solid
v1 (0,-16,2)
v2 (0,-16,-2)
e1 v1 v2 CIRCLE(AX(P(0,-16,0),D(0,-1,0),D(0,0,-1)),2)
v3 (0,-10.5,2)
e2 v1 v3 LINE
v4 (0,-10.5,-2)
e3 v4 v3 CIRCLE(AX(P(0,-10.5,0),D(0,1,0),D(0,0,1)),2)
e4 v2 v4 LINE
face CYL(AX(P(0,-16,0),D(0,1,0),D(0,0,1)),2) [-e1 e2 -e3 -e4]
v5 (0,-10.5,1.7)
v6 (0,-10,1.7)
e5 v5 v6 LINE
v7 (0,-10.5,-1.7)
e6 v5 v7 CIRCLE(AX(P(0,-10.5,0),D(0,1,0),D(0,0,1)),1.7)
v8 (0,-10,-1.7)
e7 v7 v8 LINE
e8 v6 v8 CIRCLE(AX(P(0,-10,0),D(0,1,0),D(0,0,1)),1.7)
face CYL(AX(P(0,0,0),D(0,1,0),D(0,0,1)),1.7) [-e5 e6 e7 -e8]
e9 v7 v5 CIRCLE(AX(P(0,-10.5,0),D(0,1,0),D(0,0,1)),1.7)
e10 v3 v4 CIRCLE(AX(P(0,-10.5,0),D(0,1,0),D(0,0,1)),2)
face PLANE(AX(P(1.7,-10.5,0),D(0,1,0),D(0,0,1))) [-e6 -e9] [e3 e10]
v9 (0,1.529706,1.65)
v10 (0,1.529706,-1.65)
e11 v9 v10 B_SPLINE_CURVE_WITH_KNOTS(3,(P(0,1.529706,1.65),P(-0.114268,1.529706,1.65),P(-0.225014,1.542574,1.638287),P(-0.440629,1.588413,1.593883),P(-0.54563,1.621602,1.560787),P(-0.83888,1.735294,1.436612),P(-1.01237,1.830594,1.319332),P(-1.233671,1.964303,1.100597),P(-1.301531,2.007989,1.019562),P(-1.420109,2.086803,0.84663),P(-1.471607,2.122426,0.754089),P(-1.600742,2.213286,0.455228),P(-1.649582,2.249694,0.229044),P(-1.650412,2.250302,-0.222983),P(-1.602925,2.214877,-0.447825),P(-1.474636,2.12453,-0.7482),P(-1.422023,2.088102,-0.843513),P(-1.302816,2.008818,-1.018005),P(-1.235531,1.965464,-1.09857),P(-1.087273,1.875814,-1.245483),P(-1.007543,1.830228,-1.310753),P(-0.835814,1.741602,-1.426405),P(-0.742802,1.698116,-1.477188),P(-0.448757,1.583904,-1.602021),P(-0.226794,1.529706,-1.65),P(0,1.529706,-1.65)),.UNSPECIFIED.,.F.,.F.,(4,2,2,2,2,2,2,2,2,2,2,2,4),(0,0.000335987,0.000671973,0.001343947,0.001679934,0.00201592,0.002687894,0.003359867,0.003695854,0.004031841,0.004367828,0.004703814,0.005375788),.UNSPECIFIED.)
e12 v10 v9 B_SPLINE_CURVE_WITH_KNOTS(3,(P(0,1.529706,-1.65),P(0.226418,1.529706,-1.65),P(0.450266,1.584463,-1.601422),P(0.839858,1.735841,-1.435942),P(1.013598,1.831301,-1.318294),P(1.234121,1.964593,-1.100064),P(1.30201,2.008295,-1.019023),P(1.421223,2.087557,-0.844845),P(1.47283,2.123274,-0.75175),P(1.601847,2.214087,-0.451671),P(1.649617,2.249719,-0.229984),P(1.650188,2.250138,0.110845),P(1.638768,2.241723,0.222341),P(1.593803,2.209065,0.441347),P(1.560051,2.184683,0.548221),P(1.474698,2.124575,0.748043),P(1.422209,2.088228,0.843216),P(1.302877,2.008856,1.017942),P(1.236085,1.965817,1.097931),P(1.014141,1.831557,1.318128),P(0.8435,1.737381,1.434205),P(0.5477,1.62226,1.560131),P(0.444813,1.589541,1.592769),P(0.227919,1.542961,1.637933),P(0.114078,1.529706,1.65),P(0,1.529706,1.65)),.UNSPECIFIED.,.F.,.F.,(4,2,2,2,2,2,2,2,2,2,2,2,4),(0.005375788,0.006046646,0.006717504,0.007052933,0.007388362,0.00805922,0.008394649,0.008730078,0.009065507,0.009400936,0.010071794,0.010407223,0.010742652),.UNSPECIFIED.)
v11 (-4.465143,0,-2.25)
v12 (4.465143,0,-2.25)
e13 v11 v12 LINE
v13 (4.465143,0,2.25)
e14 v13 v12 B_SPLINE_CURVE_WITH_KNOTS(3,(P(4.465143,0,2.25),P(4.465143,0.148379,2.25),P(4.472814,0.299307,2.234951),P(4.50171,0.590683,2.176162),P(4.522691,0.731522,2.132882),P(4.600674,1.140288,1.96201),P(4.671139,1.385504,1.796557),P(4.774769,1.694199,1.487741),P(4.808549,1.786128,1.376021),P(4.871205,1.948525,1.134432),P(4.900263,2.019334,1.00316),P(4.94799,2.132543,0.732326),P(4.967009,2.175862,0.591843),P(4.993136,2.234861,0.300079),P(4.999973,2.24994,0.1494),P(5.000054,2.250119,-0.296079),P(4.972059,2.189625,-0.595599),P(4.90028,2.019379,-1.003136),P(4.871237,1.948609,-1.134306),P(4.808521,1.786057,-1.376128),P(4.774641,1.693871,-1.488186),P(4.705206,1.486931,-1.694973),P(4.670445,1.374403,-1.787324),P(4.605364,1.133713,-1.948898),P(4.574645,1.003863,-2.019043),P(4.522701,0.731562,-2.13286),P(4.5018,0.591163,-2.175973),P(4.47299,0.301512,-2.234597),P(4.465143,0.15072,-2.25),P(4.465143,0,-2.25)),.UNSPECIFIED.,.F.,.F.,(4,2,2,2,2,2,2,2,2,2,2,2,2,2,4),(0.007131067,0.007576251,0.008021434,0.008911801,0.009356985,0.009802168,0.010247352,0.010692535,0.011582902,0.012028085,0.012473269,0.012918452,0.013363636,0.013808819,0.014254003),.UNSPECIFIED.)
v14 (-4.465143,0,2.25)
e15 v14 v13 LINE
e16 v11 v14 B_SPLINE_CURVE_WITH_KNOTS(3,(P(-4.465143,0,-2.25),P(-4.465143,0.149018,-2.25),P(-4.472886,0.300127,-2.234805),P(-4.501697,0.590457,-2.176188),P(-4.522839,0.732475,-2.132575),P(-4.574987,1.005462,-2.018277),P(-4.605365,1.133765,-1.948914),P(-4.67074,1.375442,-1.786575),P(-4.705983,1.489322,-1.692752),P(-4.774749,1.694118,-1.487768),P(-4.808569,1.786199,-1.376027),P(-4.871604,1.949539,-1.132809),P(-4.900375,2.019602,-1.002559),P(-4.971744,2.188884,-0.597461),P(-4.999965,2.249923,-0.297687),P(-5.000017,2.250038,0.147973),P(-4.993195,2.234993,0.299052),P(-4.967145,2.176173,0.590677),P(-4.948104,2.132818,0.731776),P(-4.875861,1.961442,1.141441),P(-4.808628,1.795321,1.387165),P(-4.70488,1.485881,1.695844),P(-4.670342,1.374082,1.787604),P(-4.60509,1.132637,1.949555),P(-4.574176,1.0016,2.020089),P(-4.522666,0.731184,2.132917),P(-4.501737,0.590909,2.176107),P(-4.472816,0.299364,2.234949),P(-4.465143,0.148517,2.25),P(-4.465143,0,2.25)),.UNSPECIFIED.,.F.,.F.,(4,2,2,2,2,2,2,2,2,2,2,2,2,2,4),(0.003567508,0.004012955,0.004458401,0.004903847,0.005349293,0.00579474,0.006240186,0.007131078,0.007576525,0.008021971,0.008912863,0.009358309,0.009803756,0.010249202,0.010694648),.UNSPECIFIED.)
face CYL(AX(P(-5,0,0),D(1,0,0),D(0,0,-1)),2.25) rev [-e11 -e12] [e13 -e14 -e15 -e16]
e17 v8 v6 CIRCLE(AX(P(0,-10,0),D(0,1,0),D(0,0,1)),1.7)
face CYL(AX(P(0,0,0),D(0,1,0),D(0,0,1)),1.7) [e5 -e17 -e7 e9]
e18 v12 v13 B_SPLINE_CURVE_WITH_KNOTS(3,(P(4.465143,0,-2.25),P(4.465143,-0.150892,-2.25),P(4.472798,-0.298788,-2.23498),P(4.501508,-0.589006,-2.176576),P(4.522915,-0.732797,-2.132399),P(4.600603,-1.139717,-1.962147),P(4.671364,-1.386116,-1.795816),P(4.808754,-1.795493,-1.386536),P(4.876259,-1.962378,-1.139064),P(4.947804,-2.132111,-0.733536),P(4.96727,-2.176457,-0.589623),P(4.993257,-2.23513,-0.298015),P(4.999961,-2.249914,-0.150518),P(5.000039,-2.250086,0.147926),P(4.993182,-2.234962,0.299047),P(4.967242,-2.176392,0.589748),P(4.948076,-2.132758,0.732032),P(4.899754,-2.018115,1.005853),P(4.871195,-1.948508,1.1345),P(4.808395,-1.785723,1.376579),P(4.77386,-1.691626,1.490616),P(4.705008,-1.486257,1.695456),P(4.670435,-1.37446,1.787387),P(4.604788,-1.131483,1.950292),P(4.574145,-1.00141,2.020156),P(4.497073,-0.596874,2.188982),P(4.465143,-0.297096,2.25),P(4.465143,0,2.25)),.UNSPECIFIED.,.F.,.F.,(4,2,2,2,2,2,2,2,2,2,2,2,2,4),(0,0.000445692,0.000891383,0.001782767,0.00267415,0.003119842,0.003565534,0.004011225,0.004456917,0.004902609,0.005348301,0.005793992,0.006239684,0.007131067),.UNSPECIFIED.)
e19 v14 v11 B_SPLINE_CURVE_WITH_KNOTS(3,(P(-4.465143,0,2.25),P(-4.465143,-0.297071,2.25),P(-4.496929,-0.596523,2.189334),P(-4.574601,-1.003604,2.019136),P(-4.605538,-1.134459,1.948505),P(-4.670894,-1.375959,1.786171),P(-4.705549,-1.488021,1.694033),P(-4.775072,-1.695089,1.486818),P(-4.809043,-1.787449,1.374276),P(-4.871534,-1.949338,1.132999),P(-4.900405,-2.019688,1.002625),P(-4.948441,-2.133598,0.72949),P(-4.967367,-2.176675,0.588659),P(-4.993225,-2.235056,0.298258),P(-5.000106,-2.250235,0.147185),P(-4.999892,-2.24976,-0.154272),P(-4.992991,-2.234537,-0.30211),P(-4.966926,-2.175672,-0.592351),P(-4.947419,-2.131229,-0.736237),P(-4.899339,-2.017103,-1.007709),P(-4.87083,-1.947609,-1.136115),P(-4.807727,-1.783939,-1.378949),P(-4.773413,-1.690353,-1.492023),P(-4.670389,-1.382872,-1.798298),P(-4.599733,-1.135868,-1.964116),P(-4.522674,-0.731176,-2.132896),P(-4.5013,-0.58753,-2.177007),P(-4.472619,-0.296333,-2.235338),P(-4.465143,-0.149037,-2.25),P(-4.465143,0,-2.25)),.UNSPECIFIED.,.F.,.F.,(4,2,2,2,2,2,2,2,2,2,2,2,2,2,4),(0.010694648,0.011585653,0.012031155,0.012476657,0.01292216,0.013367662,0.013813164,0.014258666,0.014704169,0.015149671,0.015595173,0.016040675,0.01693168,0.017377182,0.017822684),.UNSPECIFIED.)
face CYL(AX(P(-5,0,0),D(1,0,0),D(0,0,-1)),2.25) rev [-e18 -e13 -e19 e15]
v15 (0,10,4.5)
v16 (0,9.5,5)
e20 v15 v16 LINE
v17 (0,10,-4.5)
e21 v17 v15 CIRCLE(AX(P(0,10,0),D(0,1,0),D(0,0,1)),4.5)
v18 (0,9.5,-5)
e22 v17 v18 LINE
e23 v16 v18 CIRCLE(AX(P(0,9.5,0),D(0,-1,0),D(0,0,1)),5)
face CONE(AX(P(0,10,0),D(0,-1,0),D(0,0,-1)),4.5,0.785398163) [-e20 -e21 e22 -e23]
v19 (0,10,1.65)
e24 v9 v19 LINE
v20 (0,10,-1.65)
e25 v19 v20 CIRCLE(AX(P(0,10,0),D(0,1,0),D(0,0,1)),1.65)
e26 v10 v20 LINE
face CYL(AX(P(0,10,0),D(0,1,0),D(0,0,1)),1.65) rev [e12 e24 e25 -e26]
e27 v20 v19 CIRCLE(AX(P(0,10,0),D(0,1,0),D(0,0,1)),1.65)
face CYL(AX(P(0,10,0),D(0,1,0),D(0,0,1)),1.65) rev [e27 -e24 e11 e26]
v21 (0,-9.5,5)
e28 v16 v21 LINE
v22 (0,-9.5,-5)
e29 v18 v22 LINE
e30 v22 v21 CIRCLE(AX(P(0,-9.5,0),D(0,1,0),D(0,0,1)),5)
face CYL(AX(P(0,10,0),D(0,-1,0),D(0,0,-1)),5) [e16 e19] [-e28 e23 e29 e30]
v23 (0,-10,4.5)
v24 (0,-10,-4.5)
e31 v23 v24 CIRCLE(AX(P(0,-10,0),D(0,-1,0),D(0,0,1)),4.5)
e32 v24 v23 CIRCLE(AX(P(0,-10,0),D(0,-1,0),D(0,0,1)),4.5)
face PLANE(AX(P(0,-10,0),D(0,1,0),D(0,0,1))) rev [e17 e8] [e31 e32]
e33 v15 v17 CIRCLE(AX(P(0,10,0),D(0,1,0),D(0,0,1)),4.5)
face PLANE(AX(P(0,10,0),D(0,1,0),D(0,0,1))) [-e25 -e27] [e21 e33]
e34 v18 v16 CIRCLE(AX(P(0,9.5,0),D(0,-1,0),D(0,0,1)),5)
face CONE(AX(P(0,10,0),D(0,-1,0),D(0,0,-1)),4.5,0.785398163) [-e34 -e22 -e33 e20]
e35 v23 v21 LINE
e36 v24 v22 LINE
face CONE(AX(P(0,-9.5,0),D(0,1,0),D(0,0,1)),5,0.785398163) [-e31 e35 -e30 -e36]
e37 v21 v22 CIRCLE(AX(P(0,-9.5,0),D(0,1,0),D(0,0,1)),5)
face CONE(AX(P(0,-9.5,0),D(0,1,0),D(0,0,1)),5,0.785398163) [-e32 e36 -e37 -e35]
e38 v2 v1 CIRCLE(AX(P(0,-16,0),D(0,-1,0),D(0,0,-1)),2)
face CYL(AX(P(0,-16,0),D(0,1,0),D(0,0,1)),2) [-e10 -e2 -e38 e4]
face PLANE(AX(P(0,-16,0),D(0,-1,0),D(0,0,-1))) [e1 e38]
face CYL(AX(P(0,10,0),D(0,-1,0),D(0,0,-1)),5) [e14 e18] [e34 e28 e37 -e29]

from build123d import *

# Parameters (mm, degrees)
SKETCH1_R               = 5
BOSS_EXTRUDE1_DEPTH     = 10
SKETCH2_R               = 2
BOSS_EXTRUDE2_DEPTH     = 6
SKETCH3_W               = 0.3
SKETCH3_H               = 0.5
M4_TAPPED_HOLE1_D       = 3.3
M4_TAPPED_HOLE1_DEPTH   = 10.1
M4_TAPPED_HOLE1_TIP     = 0.991420021
CHAMFER1_SIZE           = 0.5
CUT_EXTRUDE1_DEPTH      = 18.492855685
CUT_EXTRUDE1_DEPTH_BACK = 18.492855685
SKETCH6_R               = 2.25


with BuildPart() as part:
    # Sketch1 → Boss-Extrude1 (new, symmetric)
    with BuildSketch(Plane(origin=(0, 0, 0), x_dir=(1, 0, 0), z_dir=(0, 1, 0))):
        with Locations(Location((0, 0, 0), (0, 0, 270))):
            Circle(SKETCH1_R)
    extrude(amount=BOSS_EXTRUDE1_DEPTH, both=True)

    # Sketch2 → Boss-Extrude2 (add)
    with BuildSketch(Plane.XZ.offset(10)):
        with Locations(Location((0, 0, 0), (0, 0, 90))):
            Circle(SKETCH2_R)
    extrude(amount=BOSS_EXTRUDE2_DEPTH)

    # Sketch3 → Cut-Revolve1 (revolve, cut)
    with BuildSketch(Plane.XY, mode=Mode.PRIVATE) as cut_revolve1_sk:
        with Locations((1.85, -10.25)):
            Rectangle(SKETCH3_W, SKETCH3_H)
    revolve(cut_revolve1_sk.sketch.rotate(Axis((0, 0, 0), (0, -1, 0)), 90), axis=Axis((0, 0, 0), (0, -1, 0)), mode=Mode.SUBTRACT)

    # M4 Tapped Hole1
    with Locations(Plane(origin=(0, 10, 0), x_dir=(1, 0, 0), z_dir=(0, 1, 0))):
        with Locations((0, 0)):
            Hole(M4_TAPPED_HOLE1_D / 2, depth=M4_TAPPED_HOLE1_DEPTH)
            with Locations((0, 0, -(M4_TAPPED_HOLE1_DEPTH + M4_TAPPED_HOLE1_TIP / 2))):  # 118° drill point
                Cone(0, M4_TAPPED_HOLE1_D / 2, M4_TAPPED_HOLE1_TIP, mode=Mode.SUBTRACT)

    # Chamfer1
    chamfer1_edges = [part.edges().sort_by_distance(p)[0] for p in [
        (0, -10, -5),
        (0, 10, -5),
    ]]
    chamfer(chamfer1_edges, length=CHAMFER1_SIZE)

    # Sketch6 → Cut-Extrude1 (cut, two sides: drawn at the far end of the back side and taken through both)
    with BuildSketch(Plane(origin=(0, 0, 0), x_dir=(0, 0, -1), z_dir=(1, 0, 0)).offset(-CUT_EXTRUDE1_DEPTH_BACK)):
        Circle(SKETCH6_R)
    extrude(amount=CUT_EXTRUDE1_DEPTH + CUT_EXTRUDE1_DEPTH_BACK, mode=Mode.SUBTRACT)


solid = part.part
